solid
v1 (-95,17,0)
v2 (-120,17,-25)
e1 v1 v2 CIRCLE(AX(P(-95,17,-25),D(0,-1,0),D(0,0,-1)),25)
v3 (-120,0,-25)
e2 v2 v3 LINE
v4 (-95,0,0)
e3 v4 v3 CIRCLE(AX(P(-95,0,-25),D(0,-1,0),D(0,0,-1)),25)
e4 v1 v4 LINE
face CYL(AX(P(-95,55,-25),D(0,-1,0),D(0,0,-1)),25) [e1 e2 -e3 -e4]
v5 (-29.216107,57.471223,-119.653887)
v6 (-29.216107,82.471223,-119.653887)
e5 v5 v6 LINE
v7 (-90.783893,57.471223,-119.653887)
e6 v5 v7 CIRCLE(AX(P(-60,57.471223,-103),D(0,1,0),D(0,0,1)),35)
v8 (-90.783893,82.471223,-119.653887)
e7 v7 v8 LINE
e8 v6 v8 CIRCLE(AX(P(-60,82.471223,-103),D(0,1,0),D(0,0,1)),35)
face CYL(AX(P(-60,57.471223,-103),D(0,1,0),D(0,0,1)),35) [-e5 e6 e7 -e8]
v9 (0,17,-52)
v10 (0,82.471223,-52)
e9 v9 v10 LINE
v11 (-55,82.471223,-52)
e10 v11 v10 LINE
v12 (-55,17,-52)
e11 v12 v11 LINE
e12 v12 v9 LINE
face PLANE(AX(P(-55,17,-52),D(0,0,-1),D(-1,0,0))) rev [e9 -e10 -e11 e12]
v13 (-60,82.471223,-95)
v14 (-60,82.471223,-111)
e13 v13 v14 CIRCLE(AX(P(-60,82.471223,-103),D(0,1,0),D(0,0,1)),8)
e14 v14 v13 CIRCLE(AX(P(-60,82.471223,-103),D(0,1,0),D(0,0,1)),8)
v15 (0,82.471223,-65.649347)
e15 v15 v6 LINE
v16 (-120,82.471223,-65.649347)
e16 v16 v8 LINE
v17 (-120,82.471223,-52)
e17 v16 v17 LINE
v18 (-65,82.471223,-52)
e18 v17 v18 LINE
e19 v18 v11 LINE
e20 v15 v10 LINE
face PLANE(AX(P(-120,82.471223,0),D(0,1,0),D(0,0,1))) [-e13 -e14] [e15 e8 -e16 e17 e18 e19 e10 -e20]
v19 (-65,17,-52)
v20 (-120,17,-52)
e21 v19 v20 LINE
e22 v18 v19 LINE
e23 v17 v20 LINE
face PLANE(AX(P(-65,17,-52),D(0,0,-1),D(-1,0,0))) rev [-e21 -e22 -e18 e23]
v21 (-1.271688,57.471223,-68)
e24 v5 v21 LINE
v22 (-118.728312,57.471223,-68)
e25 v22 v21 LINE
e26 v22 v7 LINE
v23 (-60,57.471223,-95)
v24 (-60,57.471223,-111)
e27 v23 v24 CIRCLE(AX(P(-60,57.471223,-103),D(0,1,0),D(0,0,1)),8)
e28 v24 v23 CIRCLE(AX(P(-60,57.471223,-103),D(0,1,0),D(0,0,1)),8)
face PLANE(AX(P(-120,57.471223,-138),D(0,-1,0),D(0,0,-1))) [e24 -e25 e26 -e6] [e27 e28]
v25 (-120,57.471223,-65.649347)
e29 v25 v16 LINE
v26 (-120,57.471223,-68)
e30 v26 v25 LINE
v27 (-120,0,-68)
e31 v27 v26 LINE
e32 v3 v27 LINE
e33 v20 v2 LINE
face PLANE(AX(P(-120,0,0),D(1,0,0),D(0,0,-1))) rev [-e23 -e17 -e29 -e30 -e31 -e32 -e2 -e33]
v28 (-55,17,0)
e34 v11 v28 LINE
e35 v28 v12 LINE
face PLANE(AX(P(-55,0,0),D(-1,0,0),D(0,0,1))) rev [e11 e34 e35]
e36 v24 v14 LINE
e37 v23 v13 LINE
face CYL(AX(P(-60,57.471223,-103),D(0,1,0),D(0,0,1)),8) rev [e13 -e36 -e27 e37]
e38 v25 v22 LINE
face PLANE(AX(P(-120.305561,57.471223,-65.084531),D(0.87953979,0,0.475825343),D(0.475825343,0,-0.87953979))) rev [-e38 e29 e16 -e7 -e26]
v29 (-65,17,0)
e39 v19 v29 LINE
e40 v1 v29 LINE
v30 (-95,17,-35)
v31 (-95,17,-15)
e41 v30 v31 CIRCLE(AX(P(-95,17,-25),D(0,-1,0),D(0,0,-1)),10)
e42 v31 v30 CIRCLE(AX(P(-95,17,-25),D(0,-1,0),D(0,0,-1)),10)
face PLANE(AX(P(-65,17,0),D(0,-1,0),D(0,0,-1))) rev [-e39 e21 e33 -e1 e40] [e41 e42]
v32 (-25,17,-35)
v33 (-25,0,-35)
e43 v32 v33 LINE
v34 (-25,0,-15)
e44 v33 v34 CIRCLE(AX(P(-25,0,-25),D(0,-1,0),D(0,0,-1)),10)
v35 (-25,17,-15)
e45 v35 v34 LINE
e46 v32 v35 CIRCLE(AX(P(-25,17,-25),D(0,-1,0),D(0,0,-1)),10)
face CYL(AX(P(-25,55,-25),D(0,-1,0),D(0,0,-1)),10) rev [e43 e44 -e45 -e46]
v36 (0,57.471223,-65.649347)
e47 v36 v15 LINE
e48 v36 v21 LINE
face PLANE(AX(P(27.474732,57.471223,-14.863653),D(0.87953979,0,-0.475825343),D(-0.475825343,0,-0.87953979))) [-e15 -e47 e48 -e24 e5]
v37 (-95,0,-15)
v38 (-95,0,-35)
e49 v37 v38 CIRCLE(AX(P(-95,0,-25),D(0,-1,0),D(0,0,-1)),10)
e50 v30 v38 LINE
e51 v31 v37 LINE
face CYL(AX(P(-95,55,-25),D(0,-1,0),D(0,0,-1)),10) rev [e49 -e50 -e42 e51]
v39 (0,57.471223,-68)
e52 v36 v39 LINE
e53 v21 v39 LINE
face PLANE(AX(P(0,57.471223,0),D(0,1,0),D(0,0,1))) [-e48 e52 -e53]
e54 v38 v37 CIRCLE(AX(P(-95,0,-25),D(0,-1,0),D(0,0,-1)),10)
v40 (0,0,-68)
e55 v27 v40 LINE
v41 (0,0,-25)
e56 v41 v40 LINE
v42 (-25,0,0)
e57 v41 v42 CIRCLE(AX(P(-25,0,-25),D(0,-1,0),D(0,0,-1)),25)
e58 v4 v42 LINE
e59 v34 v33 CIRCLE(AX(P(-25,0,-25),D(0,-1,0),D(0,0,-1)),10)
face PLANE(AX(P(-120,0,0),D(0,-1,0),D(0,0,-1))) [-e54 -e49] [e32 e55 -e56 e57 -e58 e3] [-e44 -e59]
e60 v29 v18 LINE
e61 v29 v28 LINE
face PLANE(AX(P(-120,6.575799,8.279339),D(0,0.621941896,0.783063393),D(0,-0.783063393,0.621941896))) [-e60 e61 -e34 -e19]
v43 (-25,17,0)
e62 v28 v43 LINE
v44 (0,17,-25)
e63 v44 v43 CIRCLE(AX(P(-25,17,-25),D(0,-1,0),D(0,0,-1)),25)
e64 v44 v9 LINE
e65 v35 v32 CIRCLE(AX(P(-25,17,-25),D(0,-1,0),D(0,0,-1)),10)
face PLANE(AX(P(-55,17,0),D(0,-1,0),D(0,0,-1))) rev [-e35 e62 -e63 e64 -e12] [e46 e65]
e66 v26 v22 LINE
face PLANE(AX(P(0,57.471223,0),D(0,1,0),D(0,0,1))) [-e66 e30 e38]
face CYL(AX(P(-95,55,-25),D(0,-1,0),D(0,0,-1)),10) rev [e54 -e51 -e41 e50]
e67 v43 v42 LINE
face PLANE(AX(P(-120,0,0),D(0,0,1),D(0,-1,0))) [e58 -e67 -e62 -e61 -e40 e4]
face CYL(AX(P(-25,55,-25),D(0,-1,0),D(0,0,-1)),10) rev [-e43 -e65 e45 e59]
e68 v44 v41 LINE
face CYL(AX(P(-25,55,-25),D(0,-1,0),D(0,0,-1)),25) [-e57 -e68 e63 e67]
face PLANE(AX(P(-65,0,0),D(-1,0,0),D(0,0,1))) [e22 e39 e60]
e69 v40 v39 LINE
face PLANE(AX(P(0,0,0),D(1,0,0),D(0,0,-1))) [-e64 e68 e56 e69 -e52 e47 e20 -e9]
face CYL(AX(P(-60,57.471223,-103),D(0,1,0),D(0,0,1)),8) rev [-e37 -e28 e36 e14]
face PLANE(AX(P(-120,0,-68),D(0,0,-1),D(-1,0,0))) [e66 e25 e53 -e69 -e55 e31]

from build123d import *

# Parameters (mm, degrees)
BOSS_EXTRUDE1_DEPTH = 120
CUT_EXTRUDE1_DEPTH  = 55
CUT_EXTRUDE2_DEPTH  = 55
SKETCH5_R           = 10
CUT_EXTRUDE3_DEPTH  = 55
SKETCH6_W           = 70
SKETCH6_H           = 25
BOSS_EXTRUDE2_DEPTH = 120
SKETCH7_R           = 8
CUT_EXTRUDE4_DEPTH  = 25


with BuildPart() as part:
    # Sketch1 → Boss-Extrude1 (new body)
    with BuildSketch(Plane(origin=(0, 0, 0), x_dir=(0, 0, -1), z_dir=(1, 0, 0))):
        Polygon((52, 82.471222814), (52, 17), (0, 17), align=None)
        Polygon((52, 17), (0, 17), (0, 0), (68, 0), (68, 82.471222814), (52, 82.471222814), align=None)
    extrude(amount=-BOSS_EXTRUDE1_DEPTH)

    # Sketch2 → Cut-Extrude1 (cut)
    with BuildSketch(Plane(origin=(0, 0, 0), x_dir=(0, 0, -1), z_dir=(1, 0, 0))):
        Polygon((52, 82.471222814), (0, 17), (52, 17), align=None)
    extrude(amount=-CUT_EXTRUDE1_DEPTH, mode=Mode.SUBTRACT)

    # Sketch3 → Cut-Extrude2 (cut)
    with BuildSketch(Plane.ZY.offset(120)):
        Polygon((-52, 82.471222814), (0, 17), (-52, 17), align=None)
    extrude(amount=-CUT_EXTRUDE2_DEPTH, mode=Mode.SUBTRACT)

    # Sketch5 → Cut-Extrude3 (cut)
    with BuildSketch(Plane.XZ):
        with BuildLine():
            Line((-95, 0), (-120, 0))
            Line((-120, 0), (-120, -25))
            ThreePointArc((-120, -25), (-112.67766953, -7.32233047), (-95, 0))
        make_face()
        with Locations(Location((-95, -25, 0), (0, 0, 270))):
            Circle(SKETCH5_R)
        with BuildLine():
            Line((0, 0), (-25, 0))
            ThreePointArc((-25, 0), (-7.32233047, -7.32233047), (0, -25))
            Line((0, -25), (0, 0))
        make_face()
        with Locations(Location((-25, -25, 0), (0, 0, 270))):
            Circle(SKETCH5_R)
    extrude(amount=-CUT_EXTRUDE3_DEPTH, mode=Mode.SUBTRACT)

    # Sketch6 → Boss-Extrude2 (add)
    with BuildSketch(Plane(origin=(0, 0, 0), x_dir=(0, 0, -1), z_dir=(1, 0, 0))):
        with Locations((103, 69.971222814)):
            Rectangle(SKETCH6_W, SKETCH6_H)
    extrude(amount=-BOSS_EXTRUDE2_DEPTH)

    # Sketch7 → Cut-Extrude4 (cut)
    with BuildSketch(Plane(origin=(0, 82.471222814, 0), x_dir=(1, 0, 0), z_dir=(0, 1, 0))):
        with Locations(Location((-60, 103, 0), (0, 0, 270))):
            Circle(SKETCH7_R)
        with BuildLine():
            Line((0, 138), (-60, 138))
            ThreePointArc((-60, 138), (-42.081937118, 133.065645221), (-29.216107334, 119.653887004))
            Line((-29.216107334, 119.653887004), (0, 65.649346677))
            Line((0, 65.649346677), (0, 138))
        make_face()
        with BuildLine():
            Line((-120, 138), (-120, 65.649346677))
            Line((-120, 65.649346677), (-90.783892666, 119.653887004))
            ThreePointArc((-90.783892666, 119.653887004), (-77.918062882, 133.065645221), (-60, 138))
            Line((-60, 138), (-120, 138))
        make_face()
    extrude(amount=-CUT_EXTRUDE4_DEPTH, mode=Mode.SUBTRACT)


solid = part.part
